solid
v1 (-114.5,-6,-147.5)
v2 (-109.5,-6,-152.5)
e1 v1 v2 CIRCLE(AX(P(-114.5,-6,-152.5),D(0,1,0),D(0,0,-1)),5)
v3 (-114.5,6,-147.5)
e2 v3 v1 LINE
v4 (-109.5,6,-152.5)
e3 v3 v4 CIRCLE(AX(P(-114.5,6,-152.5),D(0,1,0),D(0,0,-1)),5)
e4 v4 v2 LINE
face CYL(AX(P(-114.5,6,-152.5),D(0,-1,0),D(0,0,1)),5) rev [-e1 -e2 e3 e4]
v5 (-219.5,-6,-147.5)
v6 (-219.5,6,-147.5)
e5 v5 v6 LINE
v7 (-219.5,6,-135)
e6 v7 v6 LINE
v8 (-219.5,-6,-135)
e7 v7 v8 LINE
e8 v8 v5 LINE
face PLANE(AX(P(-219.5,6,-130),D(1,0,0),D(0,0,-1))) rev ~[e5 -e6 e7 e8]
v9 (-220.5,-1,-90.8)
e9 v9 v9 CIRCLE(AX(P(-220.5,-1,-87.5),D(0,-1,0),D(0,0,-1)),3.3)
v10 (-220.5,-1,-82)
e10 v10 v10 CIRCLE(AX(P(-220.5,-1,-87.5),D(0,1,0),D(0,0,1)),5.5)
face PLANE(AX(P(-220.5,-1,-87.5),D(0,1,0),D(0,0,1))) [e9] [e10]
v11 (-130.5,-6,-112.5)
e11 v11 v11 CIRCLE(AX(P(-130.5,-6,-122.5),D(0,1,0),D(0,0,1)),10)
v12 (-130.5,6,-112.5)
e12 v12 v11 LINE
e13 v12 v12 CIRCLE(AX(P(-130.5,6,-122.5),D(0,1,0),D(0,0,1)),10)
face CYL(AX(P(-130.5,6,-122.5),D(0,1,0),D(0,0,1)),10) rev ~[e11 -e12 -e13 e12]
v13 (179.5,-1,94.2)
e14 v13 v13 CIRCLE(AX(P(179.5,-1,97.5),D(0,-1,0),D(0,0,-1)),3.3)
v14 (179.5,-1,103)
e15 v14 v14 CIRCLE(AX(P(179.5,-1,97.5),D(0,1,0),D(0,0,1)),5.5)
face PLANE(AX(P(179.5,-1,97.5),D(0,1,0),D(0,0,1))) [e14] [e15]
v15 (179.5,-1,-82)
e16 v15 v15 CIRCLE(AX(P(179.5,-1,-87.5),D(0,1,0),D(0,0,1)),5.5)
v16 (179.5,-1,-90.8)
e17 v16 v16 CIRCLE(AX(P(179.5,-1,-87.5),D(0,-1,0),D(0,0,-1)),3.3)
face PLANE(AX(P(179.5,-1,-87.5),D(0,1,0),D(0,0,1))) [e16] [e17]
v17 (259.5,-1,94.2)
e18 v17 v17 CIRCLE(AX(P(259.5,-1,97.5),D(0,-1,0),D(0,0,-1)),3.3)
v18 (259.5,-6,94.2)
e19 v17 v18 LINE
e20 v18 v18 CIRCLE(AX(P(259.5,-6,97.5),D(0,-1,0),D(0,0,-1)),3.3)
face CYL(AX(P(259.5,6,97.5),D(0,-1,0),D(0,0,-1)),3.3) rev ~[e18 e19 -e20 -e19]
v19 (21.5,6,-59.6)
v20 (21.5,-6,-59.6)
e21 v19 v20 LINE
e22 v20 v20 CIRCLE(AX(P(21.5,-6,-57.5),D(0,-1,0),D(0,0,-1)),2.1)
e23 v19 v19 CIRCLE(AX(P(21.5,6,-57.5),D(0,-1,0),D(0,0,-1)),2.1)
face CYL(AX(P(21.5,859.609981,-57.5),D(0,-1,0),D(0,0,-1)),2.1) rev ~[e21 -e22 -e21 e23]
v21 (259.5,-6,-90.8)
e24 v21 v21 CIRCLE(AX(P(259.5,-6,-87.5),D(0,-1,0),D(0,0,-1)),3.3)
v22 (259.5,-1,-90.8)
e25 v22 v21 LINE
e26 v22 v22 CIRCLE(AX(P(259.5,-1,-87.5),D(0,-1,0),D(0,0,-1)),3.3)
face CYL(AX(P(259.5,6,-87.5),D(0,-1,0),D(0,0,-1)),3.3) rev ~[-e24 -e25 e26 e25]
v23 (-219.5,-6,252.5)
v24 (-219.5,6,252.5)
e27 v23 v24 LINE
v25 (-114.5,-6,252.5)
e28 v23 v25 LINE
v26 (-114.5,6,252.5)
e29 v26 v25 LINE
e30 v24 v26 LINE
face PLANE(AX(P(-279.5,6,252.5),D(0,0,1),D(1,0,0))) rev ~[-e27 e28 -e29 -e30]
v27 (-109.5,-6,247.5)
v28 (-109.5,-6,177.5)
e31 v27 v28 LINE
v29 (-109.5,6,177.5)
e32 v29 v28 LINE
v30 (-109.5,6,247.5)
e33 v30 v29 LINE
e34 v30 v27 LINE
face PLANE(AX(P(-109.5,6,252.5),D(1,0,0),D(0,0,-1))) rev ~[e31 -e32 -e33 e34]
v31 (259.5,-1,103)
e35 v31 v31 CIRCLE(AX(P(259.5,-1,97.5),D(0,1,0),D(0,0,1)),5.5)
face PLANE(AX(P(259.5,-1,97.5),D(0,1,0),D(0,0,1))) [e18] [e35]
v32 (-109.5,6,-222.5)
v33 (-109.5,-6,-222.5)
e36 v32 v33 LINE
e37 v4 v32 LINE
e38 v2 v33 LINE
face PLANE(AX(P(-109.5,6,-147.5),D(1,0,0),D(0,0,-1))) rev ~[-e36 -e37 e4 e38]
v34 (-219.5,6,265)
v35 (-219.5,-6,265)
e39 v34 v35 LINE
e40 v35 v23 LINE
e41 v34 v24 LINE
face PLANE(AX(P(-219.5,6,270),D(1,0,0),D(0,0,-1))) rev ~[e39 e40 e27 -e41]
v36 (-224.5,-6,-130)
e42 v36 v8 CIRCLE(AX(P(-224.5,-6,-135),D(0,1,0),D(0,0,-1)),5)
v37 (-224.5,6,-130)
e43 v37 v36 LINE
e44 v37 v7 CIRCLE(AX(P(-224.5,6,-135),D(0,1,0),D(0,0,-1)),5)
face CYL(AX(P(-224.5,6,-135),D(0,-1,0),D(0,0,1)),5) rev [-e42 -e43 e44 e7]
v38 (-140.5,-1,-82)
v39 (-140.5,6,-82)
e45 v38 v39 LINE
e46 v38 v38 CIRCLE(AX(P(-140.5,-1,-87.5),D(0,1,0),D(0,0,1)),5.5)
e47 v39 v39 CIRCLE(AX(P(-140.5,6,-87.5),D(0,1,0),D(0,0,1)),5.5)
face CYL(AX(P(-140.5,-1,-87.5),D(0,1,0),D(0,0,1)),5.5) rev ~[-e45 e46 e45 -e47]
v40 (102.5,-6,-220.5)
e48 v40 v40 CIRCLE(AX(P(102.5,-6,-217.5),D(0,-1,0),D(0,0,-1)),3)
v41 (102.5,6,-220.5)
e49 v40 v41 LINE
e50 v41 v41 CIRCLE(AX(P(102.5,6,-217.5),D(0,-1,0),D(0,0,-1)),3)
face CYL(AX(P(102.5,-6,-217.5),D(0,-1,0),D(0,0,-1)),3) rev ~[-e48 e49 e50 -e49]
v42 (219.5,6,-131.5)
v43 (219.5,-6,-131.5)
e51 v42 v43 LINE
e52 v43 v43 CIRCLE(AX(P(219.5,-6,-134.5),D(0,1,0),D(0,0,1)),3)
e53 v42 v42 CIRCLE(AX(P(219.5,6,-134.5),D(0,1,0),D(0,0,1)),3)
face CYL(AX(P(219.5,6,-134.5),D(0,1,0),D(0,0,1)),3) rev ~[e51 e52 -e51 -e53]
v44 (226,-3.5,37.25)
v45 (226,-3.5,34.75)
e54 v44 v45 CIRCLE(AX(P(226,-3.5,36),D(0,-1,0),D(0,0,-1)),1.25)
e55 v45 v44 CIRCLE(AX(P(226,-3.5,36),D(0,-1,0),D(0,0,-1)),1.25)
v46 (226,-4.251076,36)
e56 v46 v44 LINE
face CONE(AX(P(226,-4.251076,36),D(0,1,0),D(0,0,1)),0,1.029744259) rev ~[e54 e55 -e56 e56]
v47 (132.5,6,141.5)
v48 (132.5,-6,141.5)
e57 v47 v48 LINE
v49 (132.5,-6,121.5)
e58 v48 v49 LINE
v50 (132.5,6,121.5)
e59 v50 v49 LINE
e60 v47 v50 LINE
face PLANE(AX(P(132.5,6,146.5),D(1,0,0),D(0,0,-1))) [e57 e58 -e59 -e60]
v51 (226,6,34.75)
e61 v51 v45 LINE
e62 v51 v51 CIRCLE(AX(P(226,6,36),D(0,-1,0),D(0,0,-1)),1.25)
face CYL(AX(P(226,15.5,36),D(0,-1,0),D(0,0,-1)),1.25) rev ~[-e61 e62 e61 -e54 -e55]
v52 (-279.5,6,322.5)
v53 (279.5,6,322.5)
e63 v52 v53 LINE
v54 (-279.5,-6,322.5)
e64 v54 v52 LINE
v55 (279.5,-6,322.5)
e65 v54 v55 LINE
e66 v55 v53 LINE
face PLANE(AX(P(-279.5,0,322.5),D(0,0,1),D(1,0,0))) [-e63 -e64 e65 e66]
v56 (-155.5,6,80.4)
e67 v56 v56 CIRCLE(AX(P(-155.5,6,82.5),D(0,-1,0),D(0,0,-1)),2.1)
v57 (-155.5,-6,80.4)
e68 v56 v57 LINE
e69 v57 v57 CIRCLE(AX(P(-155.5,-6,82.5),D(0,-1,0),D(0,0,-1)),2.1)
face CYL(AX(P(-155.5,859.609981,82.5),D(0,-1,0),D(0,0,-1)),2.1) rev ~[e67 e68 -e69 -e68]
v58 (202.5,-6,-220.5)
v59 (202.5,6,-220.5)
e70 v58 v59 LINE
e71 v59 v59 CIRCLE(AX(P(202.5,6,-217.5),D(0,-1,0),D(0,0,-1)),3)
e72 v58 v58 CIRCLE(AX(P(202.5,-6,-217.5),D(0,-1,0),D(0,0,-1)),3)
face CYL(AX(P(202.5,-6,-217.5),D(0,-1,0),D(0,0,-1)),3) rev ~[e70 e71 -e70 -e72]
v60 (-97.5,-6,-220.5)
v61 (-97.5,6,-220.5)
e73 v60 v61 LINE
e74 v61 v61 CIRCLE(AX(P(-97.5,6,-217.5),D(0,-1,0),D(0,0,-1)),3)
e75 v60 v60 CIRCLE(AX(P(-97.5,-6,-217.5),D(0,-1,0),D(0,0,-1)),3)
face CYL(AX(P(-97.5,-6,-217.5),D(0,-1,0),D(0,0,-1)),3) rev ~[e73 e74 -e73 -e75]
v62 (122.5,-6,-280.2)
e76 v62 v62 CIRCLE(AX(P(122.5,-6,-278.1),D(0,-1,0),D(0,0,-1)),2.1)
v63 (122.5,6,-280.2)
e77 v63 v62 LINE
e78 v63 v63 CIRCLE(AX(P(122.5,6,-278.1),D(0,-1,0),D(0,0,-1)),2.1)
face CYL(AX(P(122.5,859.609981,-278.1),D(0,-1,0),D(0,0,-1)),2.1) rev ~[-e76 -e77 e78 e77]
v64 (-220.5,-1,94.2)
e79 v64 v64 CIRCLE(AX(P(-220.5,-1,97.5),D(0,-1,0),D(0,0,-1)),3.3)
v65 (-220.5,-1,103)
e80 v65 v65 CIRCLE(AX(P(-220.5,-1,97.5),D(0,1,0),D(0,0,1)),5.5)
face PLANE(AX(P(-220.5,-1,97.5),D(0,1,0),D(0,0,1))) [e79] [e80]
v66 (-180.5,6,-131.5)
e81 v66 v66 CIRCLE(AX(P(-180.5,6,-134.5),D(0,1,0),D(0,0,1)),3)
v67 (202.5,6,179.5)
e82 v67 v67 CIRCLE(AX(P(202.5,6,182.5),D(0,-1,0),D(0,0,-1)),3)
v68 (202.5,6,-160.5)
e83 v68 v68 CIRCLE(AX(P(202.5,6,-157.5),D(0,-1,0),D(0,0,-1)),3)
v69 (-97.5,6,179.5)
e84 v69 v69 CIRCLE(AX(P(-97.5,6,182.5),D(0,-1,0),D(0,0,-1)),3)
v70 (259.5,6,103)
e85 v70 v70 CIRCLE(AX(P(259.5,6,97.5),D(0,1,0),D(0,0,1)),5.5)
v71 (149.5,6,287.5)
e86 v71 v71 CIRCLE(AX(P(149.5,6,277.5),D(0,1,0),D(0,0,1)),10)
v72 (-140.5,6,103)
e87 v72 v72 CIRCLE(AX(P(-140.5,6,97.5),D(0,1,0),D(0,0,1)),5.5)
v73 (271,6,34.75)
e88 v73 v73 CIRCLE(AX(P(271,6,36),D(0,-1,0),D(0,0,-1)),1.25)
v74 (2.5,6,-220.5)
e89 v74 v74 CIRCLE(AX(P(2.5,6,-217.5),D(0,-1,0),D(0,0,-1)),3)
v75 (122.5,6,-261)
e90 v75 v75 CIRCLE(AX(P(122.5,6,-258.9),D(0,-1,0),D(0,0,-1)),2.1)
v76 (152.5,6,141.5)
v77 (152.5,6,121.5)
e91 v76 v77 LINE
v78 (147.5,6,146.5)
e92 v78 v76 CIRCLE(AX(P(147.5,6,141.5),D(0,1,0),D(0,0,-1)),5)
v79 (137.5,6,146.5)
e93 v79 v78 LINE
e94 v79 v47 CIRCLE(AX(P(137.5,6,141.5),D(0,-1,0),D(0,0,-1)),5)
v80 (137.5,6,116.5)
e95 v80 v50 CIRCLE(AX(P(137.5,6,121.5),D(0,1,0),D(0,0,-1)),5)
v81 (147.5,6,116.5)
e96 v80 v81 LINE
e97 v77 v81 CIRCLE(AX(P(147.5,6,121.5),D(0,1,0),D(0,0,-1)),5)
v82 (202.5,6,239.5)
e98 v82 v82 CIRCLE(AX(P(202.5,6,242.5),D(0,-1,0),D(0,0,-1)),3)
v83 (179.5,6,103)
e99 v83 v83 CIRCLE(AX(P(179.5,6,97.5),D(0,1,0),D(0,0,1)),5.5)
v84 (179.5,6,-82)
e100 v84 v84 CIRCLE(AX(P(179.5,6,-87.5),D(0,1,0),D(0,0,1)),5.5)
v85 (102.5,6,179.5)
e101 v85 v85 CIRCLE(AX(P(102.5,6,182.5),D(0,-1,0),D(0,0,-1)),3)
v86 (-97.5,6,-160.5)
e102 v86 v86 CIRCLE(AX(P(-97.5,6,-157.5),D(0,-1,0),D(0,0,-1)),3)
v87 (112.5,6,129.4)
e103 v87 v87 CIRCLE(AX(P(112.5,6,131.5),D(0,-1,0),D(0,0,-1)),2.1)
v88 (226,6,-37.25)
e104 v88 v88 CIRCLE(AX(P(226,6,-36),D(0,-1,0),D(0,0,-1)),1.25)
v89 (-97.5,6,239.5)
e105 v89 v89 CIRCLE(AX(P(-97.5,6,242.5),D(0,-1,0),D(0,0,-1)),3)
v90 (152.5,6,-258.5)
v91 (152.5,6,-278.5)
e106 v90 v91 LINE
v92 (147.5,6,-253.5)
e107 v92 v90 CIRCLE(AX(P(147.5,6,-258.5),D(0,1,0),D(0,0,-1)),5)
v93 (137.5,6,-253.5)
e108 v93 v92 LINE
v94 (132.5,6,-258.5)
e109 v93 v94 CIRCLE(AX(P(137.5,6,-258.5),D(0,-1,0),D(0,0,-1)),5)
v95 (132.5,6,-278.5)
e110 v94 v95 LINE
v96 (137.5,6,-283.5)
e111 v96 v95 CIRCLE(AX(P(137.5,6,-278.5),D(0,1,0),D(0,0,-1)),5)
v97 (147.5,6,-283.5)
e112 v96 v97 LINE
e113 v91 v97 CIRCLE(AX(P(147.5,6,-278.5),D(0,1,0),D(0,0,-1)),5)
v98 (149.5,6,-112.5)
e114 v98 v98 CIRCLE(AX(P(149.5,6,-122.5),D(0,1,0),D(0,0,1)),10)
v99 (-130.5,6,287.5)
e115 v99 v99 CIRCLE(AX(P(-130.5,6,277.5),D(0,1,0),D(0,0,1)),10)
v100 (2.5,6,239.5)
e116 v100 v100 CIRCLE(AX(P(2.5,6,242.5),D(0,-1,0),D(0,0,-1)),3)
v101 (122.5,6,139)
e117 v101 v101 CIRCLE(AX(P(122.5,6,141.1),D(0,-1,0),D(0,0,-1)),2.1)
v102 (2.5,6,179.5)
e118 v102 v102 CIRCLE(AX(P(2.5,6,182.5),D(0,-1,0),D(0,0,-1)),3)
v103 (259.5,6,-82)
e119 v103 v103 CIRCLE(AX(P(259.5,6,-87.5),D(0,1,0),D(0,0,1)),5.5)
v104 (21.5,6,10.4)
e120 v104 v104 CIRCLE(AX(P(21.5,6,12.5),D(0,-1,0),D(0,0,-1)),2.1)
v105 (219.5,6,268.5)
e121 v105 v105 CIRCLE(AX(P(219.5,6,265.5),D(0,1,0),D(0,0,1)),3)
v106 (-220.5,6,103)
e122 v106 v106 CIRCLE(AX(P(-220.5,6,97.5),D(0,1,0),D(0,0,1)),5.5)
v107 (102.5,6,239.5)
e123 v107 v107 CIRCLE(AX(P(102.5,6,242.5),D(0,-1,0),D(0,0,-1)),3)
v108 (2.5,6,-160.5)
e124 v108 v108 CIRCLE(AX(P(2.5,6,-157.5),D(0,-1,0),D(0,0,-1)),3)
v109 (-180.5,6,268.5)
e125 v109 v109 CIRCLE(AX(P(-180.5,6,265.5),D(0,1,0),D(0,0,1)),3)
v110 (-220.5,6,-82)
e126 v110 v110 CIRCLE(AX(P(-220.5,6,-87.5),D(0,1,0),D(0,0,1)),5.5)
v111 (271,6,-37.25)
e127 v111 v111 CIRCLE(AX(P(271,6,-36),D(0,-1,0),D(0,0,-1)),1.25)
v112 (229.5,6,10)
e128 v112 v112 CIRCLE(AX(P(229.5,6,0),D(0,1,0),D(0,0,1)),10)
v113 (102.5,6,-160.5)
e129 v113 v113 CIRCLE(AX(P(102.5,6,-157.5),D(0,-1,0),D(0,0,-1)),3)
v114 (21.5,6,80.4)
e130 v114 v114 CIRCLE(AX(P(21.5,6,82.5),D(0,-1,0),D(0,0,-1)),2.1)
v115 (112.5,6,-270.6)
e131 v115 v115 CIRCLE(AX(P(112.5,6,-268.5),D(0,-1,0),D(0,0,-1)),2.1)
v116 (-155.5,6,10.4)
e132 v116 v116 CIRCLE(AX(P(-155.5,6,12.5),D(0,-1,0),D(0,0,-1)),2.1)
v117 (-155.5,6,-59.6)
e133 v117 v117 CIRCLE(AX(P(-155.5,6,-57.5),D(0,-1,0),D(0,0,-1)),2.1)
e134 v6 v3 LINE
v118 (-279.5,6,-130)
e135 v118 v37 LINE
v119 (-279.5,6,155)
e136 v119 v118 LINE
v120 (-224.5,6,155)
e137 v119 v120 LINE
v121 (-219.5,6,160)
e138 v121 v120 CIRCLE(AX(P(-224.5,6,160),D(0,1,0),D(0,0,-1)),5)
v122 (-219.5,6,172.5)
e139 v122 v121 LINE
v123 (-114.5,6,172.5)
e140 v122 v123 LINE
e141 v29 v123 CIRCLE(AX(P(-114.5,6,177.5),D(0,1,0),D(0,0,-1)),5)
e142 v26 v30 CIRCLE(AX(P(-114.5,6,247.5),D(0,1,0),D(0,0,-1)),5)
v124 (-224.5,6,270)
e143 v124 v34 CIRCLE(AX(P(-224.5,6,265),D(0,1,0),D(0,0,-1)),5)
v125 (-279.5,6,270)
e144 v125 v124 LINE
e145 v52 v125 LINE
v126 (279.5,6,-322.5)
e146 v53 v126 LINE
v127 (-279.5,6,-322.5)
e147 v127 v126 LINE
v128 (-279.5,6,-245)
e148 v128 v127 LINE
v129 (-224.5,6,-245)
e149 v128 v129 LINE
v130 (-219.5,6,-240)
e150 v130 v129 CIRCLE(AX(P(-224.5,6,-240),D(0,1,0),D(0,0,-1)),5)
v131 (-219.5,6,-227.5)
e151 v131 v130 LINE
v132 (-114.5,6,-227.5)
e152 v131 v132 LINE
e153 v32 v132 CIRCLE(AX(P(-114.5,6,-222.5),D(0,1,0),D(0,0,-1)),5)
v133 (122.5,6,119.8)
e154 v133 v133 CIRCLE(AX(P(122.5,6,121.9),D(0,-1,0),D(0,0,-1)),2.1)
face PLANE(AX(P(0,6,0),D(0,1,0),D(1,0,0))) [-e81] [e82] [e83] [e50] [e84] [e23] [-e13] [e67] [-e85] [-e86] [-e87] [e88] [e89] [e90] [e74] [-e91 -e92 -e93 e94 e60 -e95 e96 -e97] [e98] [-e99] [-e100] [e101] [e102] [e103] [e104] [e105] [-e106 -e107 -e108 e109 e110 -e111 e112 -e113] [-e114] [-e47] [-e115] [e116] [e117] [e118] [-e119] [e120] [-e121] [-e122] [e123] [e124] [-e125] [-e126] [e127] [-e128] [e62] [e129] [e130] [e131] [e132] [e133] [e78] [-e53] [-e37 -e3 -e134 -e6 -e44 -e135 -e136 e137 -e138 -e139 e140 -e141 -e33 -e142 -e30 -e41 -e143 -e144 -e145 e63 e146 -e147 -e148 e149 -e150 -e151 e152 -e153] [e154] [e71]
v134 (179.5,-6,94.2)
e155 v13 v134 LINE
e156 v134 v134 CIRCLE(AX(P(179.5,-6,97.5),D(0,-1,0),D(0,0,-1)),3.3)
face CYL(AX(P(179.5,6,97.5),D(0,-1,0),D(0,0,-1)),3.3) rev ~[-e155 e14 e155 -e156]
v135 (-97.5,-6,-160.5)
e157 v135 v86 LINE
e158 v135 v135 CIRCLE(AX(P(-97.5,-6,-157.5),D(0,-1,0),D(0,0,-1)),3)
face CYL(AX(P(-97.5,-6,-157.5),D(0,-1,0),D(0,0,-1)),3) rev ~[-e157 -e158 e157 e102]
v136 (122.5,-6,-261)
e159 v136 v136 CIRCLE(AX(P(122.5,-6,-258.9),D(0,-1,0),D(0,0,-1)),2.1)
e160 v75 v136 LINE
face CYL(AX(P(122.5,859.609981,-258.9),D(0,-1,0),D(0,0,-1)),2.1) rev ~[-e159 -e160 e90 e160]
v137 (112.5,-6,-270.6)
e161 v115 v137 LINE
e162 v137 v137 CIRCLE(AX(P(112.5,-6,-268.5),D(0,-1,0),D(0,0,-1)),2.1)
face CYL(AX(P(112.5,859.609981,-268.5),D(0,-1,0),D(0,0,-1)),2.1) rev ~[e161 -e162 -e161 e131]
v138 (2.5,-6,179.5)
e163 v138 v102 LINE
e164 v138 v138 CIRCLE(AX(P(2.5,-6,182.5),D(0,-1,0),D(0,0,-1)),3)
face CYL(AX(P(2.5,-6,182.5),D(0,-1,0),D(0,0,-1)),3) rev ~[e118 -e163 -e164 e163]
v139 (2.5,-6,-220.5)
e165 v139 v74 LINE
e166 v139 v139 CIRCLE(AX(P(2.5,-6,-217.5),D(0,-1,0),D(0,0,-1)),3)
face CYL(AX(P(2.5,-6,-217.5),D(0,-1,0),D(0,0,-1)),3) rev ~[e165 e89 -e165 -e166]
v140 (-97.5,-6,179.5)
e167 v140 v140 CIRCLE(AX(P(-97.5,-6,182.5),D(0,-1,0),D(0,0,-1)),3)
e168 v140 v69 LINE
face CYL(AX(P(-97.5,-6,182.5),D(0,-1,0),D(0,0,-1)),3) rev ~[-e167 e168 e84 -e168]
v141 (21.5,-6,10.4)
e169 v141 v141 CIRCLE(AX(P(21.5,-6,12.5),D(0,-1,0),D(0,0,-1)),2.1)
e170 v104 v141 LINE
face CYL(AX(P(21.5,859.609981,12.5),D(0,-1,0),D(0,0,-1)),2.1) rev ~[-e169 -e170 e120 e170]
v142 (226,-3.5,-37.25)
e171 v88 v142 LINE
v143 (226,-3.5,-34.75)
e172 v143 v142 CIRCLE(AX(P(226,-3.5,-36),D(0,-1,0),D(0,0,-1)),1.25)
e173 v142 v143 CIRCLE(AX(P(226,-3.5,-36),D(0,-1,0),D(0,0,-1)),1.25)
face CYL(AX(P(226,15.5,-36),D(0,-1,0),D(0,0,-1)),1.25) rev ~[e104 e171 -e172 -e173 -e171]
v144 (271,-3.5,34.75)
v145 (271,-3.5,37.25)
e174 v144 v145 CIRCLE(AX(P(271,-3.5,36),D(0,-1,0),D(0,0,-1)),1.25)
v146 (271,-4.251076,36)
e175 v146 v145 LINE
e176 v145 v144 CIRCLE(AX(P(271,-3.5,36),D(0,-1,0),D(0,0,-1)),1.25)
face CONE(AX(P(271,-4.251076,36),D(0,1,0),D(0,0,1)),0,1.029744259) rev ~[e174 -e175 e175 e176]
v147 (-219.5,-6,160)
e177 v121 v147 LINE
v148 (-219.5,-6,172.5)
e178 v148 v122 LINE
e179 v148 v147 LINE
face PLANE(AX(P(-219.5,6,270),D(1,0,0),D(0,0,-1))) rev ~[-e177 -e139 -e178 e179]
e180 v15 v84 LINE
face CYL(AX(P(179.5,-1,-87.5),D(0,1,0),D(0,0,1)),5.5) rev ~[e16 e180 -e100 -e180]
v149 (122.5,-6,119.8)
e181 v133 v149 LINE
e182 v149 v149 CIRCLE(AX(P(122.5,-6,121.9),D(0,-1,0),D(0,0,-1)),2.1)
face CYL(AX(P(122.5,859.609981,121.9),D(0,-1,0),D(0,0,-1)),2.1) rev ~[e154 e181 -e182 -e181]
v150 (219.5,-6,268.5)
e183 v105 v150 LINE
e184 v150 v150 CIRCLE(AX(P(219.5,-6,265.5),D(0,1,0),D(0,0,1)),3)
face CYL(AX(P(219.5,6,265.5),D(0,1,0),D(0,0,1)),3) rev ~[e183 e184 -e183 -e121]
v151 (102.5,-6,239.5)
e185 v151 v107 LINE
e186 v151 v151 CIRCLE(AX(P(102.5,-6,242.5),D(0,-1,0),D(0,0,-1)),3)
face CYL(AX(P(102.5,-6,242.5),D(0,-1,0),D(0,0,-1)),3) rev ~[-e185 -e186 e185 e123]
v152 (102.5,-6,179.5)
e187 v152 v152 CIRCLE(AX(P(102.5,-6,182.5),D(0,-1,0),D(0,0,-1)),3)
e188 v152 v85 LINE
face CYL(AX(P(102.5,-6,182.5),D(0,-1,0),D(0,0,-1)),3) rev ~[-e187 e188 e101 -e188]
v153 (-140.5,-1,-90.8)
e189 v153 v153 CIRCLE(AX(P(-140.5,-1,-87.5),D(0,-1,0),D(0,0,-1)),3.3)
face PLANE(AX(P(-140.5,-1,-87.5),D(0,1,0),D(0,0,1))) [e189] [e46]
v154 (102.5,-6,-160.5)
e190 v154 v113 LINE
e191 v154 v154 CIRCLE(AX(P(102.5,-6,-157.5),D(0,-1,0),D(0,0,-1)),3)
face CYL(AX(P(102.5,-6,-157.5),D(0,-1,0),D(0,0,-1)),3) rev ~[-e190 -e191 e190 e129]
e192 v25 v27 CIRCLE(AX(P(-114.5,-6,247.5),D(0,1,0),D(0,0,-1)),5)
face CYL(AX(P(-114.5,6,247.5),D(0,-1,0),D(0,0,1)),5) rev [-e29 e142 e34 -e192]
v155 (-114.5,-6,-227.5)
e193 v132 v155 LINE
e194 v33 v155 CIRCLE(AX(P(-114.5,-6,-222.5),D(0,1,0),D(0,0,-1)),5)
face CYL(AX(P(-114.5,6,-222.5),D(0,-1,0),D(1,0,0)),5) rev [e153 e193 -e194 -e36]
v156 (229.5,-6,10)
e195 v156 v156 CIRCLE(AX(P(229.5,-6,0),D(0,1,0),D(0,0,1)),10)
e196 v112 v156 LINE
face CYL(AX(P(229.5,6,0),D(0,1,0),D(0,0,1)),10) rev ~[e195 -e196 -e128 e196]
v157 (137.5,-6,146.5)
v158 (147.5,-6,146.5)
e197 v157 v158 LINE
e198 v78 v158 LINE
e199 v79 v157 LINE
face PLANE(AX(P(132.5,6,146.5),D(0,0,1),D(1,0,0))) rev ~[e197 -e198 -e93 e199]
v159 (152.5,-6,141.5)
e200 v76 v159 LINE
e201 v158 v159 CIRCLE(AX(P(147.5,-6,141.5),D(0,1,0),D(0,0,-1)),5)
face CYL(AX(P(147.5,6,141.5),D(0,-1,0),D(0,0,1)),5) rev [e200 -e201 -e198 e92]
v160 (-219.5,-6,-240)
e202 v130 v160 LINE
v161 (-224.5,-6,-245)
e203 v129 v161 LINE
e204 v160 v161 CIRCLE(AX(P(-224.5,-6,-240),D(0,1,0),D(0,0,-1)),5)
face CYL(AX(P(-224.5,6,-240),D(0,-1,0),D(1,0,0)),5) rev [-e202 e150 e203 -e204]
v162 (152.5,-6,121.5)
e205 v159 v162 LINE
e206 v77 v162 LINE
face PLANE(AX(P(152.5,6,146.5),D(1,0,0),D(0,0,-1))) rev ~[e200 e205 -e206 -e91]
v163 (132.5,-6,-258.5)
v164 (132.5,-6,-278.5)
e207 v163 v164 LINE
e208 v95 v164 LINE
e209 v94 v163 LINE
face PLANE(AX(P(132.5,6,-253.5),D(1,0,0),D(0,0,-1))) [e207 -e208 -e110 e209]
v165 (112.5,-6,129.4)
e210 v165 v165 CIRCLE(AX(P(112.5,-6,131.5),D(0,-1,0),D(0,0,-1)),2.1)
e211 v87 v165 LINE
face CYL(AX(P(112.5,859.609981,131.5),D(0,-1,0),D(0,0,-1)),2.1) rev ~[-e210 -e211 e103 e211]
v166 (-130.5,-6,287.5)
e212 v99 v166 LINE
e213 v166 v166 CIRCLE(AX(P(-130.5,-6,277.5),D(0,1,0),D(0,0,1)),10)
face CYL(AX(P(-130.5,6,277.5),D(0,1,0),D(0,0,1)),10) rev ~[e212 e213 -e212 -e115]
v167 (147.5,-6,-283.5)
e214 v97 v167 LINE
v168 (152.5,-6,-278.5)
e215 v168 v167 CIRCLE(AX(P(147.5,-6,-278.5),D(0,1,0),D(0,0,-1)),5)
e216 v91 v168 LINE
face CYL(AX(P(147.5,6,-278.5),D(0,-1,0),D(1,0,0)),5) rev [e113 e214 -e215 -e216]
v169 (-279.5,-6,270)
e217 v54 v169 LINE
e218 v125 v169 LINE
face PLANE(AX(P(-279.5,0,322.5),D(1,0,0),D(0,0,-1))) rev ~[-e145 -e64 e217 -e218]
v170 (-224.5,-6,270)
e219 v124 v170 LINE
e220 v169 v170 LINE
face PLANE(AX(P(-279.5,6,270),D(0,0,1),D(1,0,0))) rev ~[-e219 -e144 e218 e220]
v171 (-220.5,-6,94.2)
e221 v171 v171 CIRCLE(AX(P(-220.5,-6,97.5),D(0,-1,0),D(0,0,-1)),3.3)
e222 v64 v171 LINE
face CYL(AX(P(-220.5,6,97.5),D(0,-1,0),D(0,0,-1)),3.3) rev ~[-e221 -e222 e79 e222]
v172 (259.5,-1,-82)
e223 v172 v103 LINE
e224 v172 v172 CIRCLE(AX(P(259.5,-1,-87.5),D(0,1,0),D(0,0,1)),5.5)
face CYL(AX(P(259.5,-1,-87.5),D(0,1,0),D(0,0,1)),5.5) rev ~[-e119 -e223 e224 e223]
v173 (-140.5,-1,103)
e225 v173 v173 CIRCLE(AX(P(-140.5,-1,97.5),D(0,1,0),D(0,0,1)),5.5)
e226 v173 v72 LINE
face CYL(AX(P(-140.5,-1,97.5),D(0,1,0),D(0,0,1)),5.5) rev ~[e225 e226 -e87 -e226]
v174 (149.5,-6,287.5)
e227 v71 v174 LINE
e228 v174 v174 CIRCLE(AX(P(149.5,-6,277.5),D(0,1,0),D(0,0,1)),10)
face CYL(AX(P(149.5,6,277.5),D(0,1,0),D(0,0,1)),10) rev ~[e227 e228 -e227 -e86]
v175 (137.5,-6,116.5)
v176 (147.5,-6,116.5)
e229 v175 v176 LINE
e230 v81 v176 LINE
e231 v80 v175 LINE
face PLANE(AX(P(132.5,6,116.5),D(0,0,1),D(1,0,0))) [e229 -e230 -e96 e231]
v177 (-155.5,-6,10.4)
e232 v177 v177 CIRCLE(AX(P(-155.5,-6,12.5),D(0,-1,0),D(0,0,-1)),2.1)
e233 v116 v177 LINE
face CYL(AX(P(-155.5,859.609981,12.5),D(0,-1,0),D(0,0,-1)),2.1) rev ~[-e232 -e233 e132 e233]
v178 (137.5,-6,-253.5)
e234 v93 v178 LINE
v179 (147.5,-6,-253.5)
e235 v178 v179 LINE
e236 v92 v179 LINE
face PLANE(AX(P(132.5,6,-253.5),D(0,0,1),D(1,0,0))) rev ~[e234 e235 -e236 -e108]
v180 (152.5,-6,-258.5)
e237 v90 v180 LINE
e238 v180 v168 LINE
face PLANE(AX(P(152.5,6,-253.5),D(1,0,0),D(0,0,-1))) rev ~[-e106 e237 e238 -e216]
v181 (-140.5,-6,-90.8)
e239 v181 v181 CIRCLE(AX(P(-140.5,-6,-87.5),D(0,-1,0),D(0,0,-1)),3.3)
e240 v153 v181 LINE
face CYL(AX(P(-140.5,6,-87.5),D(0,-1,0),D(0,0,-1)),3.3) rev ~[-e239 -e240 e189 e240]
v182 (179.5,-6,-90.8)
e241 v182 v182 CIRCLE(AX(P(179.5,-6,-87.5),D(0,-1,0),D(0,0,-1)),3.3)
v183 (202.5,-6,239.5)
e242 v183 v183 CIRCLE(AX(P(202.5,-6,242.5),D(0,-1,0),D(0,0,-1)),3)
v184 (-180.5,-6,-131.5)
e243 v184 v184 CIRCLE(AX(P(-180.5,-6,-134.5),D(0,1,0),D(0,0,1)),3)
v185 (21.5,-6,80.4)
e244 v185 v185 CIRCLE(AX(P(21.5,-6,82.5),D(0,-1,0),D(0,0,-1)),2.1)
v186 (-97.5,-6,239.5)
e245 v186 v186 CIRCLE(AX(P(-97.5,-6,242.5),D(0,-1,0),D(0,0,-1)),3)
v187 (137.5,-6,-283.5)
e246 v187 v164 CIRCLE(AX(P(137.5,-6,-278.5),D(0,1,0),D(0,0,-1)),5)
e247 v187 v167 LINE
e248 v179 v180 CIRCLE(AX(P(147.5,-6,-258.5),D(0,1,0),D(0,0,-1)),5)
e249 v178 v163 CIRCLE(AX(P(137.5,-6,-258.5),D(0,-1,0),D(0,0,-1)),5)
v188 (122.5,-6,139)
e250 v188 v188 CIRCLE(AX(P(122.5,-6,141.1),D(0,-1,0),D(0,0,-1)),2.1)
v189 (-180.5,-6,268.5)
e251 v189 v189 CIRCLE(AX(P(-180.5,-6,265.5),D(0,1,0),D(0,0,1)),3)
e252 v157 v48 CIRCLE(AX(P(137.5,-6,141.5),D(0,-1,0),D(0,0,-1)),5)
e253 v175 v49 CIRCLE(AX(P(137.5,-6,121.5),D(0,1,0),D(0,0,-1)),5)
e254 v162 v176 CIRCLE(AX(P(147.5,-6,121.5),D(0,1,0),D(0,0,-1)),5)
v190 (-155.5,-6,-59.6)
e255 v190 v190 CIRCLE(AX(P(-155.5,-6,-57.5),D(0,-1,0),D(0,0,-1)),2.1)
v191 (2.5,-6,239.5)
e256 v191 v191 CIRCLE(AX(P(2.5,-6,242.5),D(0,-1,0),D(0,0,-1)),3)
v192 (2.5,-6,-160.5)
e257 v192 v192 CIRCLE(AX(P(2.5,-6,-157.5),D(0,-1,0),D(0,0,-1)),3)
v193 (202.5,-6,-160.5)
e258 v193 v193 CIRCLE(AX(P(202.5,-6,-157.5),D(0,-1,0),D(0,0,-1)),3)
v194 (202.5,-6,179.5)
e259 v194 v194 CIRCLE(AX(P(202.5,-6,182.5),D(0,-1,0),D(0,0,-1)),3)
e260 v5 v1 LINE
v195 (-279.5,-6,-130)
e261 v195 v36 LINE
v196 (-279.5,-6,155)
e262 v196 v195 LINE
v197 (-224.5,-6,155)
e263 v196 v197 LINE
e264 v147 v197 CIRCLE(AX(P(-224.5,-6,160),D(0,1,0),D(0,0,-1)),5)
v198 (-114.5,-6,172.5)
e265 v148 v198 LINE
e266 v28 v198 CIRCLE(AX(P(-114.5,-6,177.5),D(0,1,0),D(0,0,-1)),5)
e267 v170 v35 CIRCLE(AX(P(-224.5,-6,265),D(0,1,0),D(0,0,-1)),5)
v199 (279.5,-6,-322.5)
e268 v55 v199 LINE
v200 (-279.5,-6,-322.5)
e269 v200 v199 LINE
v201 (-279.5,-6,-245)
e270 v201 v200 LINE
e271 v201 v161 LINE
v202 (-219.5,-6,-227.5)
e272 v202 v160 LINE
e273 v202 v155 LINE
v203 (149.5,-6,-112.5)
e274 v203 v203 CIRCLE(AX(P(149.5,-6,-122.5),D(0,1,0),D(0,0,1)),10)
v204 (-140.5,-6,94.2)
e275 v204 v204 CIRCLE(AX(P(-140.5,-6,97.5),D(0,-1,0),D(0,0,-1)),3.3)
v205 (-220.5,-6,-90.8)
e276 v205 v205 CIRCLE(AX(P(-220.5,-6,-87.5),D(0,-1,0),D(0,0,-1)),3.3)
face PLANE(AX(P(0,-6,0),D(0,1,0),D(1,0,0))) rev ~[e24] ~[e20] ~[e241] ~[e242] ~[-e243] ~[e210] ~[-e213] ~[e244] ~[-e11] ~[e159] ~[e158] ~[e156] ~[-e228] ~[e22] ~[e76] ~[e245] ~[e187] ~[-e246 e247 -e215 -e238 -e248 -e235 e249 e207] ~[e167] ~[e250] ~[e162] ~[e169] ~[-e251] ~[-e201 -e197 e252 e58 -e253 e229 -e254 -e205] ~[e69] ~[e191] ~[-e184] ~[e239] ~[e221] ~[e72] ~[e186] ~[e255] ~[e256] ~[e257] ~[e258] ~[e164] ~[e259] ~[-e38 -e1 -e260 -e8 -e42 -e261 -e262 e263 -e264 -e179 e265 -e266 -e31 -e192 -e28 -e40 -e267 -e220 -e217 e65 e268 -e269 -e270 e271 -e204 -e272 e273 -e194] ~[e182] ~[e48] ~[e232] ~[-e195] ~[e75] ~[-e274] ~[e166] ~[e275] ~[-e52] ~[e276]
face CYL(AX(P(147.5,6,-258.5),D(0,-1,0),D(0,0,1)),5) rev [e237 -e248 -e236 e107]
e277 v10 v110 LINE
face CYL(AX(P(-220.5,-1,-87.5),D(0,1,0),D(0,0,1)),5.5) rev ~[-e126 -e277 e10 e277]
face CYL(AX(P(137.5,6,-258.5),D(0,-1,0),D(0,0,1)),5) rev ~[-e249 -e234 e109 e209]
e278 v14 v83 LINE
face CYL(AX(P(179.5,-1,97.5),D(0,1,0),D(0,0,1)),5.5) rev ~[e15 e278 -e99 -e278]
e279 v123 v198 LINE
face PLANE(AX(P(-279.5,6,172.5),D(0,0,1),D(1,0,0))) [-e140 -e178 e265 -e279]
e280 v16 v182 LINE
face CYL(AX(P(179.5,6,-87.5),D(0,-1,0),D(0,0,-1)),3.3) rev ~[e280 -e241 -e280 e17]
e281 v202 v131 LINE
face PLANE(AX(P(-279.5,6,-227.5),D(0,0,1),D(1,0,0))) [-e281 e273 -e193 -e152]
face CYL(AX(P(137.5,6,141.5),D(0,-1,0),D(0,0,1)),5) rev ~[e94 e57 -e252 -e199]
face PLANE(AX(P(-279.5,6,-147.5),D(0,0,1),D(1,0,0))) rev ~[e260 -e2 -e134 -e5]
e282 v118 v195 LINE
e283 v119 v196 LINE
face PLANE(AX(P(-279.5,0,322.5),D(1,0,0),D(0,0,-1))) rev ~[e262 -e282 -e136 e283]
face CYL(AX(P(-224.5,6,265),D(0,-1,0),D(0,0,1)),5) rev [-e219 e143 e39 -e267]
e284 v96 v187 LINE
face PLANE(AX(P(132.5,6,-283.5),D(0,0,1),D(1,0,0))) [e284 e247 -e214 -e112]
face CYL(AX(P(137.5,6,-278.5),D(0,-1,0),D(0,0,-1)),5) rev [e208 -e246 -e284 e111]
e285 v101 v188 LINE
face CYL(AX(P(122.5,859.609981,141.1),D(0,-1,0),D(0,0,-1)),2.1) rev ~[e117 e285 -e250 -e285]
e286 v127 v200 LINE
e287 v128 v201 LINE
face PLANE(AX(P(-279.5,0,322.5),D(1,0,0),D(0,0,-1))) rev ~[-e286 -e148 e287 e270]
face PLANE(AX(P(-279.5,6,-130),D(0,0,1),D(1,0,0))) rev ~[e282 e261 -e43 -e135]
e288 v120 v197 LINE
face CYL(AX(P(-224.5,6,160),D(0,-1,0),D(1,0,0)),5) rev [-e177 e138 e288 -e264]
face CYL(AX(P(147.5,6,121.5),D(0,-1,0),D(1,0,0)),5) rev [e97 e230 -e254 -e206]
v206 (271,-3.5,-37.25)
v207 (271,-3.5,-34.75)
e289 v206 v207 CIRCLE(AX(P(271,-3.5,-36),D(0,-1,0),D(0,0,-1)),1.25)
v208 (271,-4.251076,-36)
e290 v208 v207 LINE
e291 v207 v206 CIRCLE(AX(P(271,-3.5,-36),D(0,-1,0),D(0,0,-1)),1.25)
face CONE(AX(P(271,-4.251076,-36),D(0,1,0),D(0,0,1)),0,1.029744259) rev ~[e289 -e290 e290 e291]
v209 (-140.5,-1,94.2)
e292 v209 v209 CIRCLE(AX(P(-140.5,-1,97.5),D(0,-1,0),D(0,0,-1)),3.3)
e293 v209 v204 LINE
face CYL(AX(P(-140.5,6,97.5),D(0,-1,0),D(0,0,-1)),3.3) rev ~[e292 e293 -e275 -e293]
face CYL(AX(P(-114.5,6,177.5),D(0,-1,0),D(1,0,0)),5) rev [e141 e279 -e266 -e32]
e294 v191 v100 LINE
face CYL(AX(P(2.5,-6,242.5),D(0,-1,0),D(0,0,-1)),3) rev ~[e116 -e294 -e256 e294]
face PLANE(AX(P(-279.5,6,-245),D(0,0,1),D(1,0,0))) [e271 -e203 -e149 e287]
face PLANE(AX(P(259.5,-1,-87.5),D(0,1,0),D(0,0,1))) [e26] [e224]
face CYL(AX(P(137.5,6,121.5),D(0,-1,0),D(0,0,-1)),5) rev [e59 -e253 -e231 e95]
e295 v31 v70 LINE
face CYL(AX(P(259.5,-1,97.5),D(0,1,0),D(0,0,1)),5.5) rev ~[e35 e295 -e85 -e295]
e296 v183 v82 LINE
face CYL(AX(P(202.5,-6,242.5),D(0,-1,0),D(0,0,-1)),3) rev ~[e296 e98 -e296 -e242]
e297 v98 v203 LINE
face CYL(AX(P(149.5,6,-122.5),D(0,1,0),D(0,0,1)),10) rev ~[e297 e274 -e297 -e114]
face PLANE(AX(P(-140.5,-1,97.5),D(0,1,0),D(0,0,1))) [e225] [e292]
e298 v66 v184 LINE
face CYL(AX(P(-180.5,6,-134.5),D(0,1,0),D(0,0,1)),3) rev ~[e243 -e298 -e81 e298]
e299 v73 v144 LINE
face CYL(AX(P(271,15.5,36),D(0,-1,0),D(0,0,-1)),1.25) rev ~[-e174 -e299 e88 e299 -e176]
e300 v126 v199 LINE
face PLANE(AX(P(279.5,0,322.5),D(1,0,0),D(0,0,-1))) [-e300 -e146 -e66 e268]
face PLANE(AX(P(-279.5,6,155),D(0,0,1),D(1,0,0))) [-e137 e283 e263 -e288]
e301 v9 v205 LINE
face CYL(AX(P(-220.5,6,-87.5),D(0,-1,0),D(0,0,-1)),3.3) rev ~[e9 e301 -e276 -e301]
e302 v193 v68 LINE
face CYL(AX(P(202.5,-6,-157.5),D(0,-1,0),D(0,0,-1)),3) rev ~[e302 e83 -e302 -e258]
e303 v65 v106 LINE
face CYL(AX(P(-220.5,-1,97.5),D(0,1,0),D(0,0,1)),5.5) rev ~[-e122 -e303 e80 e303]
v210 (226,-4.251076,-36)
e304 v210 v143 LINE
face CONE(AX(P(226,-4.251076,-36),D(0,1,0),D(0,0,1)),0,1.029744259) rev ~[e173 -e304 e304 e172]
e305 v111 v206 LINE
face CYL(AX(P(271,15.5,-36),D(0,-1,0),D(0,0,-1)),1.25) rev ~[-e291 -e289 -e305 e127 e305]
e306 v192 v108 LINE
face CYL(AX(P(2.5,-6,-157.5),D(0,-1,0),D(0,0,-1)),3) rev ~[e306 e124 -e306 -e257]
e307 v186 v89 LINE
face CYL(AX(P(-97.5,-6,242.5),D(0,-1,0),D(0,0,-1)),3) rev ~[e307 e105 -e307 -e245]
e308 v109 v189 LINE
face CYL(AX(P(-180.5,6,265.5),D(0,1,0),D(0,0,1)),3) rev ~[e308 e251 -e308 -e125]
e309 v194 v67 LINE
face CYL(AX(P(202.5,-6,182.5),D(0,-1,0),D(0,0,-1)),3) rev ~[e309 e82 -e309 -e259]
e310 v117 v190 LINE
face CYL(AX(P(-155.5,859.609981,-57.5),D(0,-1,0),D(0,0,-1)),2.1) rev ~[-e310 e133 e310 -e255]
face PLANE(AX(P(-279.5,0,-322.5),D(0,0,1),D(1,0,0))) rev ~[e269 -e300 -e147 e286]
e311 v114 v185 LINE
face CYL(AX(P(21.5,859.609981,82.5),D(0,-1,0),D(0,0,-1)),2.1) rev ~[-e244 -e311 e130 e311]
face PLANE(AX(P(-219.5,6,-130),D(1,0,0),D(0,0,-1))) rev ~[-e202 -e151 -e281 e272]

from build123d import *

# Parameters (mm, degrees)
SKETCH1_W                                         = 559
SKETCH1_H                                         = 645
EXTRUDE1_DEPTH                                    = 6
SKETCH2_W                                         = 170
SKETCH2_H                                         = 80
CUT_EXTRUDE1_DEPTH                                = 427.931493334
SKETCH3_W                                         = 60
SKETCH3_H                                         = 115
CUT_EXTRUDE2_DEPTH                                = 427.931493334
FILLET1_R                                         = 5
M6_SOCKET_HEAD_CAP_SCREW_COUNTERBORE1_D           = 6.6
M6_SOCKET_HEAD_CAP_SCREW_COUNTERBORE1_CBORE_D     = 11
M6_SOCKET_HEAD_CAP_SCREW_COUNTERBORE1_CBORE_DEPTH = 7
M3_TAPPED_HOLE1_D                                 = 2.5
M3_TAPPED_HOLE1_DEPTH                             = 9.5
M3_TAPPED_HOLE1_TIP                               = 0.751075774
M5_TAPPED_HOLE1_D                                 = 4.2
M5_TAPPED_HOLE2_D                                 = 4.2
SKETCH12_W                                        = 20
SKETCH12_H                                        = 30
CUT_EXTRUDE3_DEPTH                                = 427.931493334
FILLET2_R                                         = 5
SKETCH13_R                                        = 10
CUT_EXTRUDE4_DEPTH                                = 427.931493334
SKETCH14_R                                        = 10
CUT_EXTRUDE5_DEPTH                                = 427.931493334
LINEAR_PATTERN1_COUNT                             = 2
LINEAR_PATTERN1_PITCH                             = 400
SKETCH15_R                                        = 3
CUT_EXTRUDE6_DEPTH                                = 427.931493334
SKETCH17_R                                        = 3
CUT_EXTRUDE7_DEPTH                                = 427.931493334


with BuildPart() as part:
    # Sketch1 → Extrude1 (new, symmetric)
    with BuildSketch(Plane(origin=(0, 0, 0), x_dir=(1, 0, 0), z_dir=(0, 1, 0))):
        Rectangle(SKETCH1_W, SKETCH1_H)
    extrude(amount=EXTRUDE1_DEPTH, both=True)

    # Sketch2 → Cut-Extrude1 (cut, through all)
    with BuildSketch(Plane(origin=(0, 6, 0), x_dir=(1, 0, 0), z_dir=(0, 1, 0))):
        with Locations((-194.5, -212.5)):
            Rectangle(SKETCH2_W, SKETCH2_H)
        with Locations((-194.5, 187.5)):
            Rectangle(SKETCH2_W, SKETCH2_H)
    extrude(amount=-CUT_EXTRUDE1_DEPTH, mode=Mode.SUBTRACT)

    # Sketch3 → Cut-Extrude2 (cut, through all)
    with BuildSketch(Plane(origin=(0, 6, 0), x_dir=(1, 0, 0), z_dir=(0, 1, 0))):
        with Locations((-249.5, 187.5)):
            Rectangle(SKETCH3_W, SKETCH3_H)
        with Locations((-249.5, -212.5)):
            Rectangle(SKETCH3_W, SKETCH3_H)
    extrude(amount=-CUT_EXTRUDE2_DEPTH, mode=Mode.SUBTRACT)

    # Fillet1
    fillet1_edges = [part.edges().sort_by_distance(p)[0] for p in [
        (-109.5, 0, 172.5),
        (-109.5, 0, 252.5),
        (-109.5, 0, -147.5),
        (-109.5, 0, -227.5),
        (-219.5, 0, -245),
        (-219.5, 0, -130),
        (-219.5, 0, 155),
        (-219.5, 0, 270),
    ]]
    fillet(fillet1_edges, radius=FILLET1_R)

    # M6 Socket Head Cap Screw Counterbore1 (through all)
    with Locations(Plane(origin=(-220.5, 6, -87.5), x_dir=(0, 0, 1), z_dir=(0, 1, 0))):
        with Locations((0, 0), (185, 0), (185, 80), (0, 80), (185, 400), (185, 480), (0, 400), (0, 480)):
            CounterBoreHole(M6_SOCKET_HEAD_CAP_SCREW_COUNTERBORE1_D / 2, M6_SOCKET_HEAD_CAP_SCREW_COUNTERBORE1_CBORE_D / 2, M6_SOCKET_HEAD_CAP_SCREW_COUNTERBORE1_CBORE_DEPTH)

    # M3 Tapped Hole1
    with Locations(Plane(origin=(271, 6, -36), x_dir=(0, 0, 1), z_dir=(0, 1, 0))):
        with Locations((0, 0), (0, -45), (72, 0), (72, -45)):
            Hole(M3_TAPPED_HOLE1_D / 2, depth=M3_TAPPED_HOLE1_DEPTH)
            with Locations((0, 0, -(M3_TAPPED_HOLE1_DEPTH + M3_TAPPED_HOLE1_TIP / 2))):  # 118° drill point
                Cone(0, M3_TAPPED_HOLE1_D / 2, M3_TAPPED_HOLE1_TIP, mode=Mode.SUBTRACT)

    # M5 Tapped Hole1 (through all)
    with Locations(Plane(origin=(122.5, 6, 141.1), x_dir=(0, 0, 1), z_dir=(0, 1, 0))):
        with Locations((0, 0), (-9.6, -10), (-19.2, 0), (-409.6, -10), (-400, 0), (-419.2, 0)):
            Hole(M5_TAPPED_HOLE1_D / 2)

    # M5 Tapped Hole2 (through all)
    with Locations(Plane(origin=(-155.5, 6, 82.5), x_dir=(0, 0, 1), z_dir=(0, 1, 0))):
        with Locations((0, 0), (-140, 0), (0, 177), (-140, 177), (-70, 0), (-70, 177)):
            Hole(M5_TAPPED_HOLE2_D / 2)

    # Sketch12 → Cut-Extrude3 (cut, through all)
    with BuildSketch(Plane(origin=(0, 6, 0), x_dir=(1, 0, 0), z_dir=(0, 1, 0))):
        with Locations((142.5, -131.5)):
            Rectangle(SKETCH12_W, SKETCH12_H)
        with Locations((142.5, 268.5)):
            Rectangle(SKETCH12_W, SKETCH12_H)
    extrude(amount=-CUT_EXTRUDE3_DEPTH, mode=Mode.SUBTRACT)

    # Fillet2
    fillet2_edges = [part.edges().sort_by_distance(p)[0] for p in [
        (132.5, 0, -253.5),
        (132.5, 0, -283.5),
        (152.5, 0, -283.5),
        (152.5, 0, -253.5),
        (132.5, 0, 116.5),
        (152.5, 0, 116.5),
        (152.5, 0, 146.5),
        (132.5, 0, 146.5),
    ]]
    fillet(fillet2_edges, radius=FILLET2_R)

    # Sketch13 → Cut-Extrude4 (cut, through all)
    with BuildSketch(Plane(origin=(0, 6, 0), x_dir=(1, 0, 0), z_dir=(0, 1, 0))):
        with Locations(Location((229.5, 0, 0), (0, 0, 270))):
            Circle(SKETCH13_R)
    extrude(amount=-CUT_EXTRUDE4_DEPTH, mode=Mode.SUBTRACT)

    # Sketch14 → Cut-Extrude5 (cut, through all)
    with BuildSketch(Plane(origin=(0, 6, 0), x_dir=(1, 0, 0), z_dir=(0, 1, 0))):
        with Locations(Location((-130.5, 122.5, 0), (0, 0, 270))):
            Circle(SKETCH14_R)
        with Locations(Location((149.5, 122.5, 0), (0, 0, 270))):
            Circle(SKETCH14_R)
    cut_extrude5 = extrude(amount=-CUT_EXTRUDE5_DEPTH, mode=Mode.SUBTRACT)

    # Linear Pattern1: Cut-Extrude5 ×2
    with Locations(*[(0, 0, i * LINEAR_PATTERN1_PITCH) for i in range(1, LINEAR_PATTERN1_COUNT)]):
        add(cut_extrude5, mode=Mode.SUBTRACT)

    # Sketch15 → Cut-Extrude6 (cut, through all)
    with BuildSketch(Plane(origin=(0, 6, 0), x_dir=(1, 0, 0), z_dir=(0, 1, 0))):
        with Locations(Location((-180.5, 134.5, 0), (0, 0, 270))):
            Circle(SKETCH15_R)
        with Locations(Location((219.5, 134.5, 0), (0, 0, 270))):
            Circle(SKETCH15_R)
        with Locations(Location((219.5, -265.5, 0), (0, 0, 270))):
            Circle(SKETCH15_R)
        with Locations(Location((-180.5, -265.5, 0), (0, 0, 270))):
            Circle(SKETCH15_R)
    extrude(amount=-CUT_EXTRUDE6_DEPTH, mode=Mode.SUBTRACT)

    # Sketch17 → Cut-Extrude7 (cut, through all)
    with BuildSketch(Plane.XZ.offset(6)):
        with Locations(Location((202.5, 242.5, 0), (0, 0, 270))):
            Circle(SKETCH17_R)
        with Locations(Location((202.5, 182.5, 0), (0, 0, 270))):
            Circle(SKETCH17_R)
        with Locations(Location((102.5, 242.5, 0), (0, 0, 270))):
            Circle(SKETCH17_R)
        with Locations(Location((102.5, 182.5, 0), (0, 0, 270))):
            Circle(SKETCH17_R)
        with Locations(Location((2.5, 242.5, 0), (0, 0, 270))):
            Circle(SKETCH17_R)
        with Locations(Location((2.5, 182.5, 0), (0, 0, 270))):
            Circle(SKETCH17_R)
        with Locations(Location((-97.5, 242.5, 0), (0, 0, 270))):
            Circle(SKETCH17_R)
        with Locations(Location((-97.5, 182.5, 0), (0, 0, 270))):
            Circle(SKETCH17_R)
        with Locations(Location((-97.5, -157.5, 0), (0, 0, 270))):
            Circle(SKETCH17_R)
        with Locations(Location((-97.5, -217.5, 0), (0, 0, 270))):
            Circle(SKETCH17_R)
        with Locations(Location((2.5, -157.5, 0), (0, 0, 270))):
            Circle(SKETCH17_R)
        with Locations(Location((2.5, -217.5, 0), (0, 0, 270))):
            Circle(SKETCH17_R)
        with Locations(Location((102.5, -157.5, 0), (0, 0, 270))):
            Circle(SKETCH17_R)
        with Locations(Location((102.5, -217.5, 0), (0, 0, 270))):
            Circle(SKETCH17_R)
        with Locations(Location((202.5, -157.5, 0), (0, 0, 270))):
            Circle(SKETCH17_R)
        with Locations(Location((202.5, -217.5, 0), (0, 0, 270))):
            Circle(SKETCH17_R)
    extrude(amount=-CUT_EXTRUDE7_DEPTH, mode=Mode.SUBTRACT)


solid = part.part
